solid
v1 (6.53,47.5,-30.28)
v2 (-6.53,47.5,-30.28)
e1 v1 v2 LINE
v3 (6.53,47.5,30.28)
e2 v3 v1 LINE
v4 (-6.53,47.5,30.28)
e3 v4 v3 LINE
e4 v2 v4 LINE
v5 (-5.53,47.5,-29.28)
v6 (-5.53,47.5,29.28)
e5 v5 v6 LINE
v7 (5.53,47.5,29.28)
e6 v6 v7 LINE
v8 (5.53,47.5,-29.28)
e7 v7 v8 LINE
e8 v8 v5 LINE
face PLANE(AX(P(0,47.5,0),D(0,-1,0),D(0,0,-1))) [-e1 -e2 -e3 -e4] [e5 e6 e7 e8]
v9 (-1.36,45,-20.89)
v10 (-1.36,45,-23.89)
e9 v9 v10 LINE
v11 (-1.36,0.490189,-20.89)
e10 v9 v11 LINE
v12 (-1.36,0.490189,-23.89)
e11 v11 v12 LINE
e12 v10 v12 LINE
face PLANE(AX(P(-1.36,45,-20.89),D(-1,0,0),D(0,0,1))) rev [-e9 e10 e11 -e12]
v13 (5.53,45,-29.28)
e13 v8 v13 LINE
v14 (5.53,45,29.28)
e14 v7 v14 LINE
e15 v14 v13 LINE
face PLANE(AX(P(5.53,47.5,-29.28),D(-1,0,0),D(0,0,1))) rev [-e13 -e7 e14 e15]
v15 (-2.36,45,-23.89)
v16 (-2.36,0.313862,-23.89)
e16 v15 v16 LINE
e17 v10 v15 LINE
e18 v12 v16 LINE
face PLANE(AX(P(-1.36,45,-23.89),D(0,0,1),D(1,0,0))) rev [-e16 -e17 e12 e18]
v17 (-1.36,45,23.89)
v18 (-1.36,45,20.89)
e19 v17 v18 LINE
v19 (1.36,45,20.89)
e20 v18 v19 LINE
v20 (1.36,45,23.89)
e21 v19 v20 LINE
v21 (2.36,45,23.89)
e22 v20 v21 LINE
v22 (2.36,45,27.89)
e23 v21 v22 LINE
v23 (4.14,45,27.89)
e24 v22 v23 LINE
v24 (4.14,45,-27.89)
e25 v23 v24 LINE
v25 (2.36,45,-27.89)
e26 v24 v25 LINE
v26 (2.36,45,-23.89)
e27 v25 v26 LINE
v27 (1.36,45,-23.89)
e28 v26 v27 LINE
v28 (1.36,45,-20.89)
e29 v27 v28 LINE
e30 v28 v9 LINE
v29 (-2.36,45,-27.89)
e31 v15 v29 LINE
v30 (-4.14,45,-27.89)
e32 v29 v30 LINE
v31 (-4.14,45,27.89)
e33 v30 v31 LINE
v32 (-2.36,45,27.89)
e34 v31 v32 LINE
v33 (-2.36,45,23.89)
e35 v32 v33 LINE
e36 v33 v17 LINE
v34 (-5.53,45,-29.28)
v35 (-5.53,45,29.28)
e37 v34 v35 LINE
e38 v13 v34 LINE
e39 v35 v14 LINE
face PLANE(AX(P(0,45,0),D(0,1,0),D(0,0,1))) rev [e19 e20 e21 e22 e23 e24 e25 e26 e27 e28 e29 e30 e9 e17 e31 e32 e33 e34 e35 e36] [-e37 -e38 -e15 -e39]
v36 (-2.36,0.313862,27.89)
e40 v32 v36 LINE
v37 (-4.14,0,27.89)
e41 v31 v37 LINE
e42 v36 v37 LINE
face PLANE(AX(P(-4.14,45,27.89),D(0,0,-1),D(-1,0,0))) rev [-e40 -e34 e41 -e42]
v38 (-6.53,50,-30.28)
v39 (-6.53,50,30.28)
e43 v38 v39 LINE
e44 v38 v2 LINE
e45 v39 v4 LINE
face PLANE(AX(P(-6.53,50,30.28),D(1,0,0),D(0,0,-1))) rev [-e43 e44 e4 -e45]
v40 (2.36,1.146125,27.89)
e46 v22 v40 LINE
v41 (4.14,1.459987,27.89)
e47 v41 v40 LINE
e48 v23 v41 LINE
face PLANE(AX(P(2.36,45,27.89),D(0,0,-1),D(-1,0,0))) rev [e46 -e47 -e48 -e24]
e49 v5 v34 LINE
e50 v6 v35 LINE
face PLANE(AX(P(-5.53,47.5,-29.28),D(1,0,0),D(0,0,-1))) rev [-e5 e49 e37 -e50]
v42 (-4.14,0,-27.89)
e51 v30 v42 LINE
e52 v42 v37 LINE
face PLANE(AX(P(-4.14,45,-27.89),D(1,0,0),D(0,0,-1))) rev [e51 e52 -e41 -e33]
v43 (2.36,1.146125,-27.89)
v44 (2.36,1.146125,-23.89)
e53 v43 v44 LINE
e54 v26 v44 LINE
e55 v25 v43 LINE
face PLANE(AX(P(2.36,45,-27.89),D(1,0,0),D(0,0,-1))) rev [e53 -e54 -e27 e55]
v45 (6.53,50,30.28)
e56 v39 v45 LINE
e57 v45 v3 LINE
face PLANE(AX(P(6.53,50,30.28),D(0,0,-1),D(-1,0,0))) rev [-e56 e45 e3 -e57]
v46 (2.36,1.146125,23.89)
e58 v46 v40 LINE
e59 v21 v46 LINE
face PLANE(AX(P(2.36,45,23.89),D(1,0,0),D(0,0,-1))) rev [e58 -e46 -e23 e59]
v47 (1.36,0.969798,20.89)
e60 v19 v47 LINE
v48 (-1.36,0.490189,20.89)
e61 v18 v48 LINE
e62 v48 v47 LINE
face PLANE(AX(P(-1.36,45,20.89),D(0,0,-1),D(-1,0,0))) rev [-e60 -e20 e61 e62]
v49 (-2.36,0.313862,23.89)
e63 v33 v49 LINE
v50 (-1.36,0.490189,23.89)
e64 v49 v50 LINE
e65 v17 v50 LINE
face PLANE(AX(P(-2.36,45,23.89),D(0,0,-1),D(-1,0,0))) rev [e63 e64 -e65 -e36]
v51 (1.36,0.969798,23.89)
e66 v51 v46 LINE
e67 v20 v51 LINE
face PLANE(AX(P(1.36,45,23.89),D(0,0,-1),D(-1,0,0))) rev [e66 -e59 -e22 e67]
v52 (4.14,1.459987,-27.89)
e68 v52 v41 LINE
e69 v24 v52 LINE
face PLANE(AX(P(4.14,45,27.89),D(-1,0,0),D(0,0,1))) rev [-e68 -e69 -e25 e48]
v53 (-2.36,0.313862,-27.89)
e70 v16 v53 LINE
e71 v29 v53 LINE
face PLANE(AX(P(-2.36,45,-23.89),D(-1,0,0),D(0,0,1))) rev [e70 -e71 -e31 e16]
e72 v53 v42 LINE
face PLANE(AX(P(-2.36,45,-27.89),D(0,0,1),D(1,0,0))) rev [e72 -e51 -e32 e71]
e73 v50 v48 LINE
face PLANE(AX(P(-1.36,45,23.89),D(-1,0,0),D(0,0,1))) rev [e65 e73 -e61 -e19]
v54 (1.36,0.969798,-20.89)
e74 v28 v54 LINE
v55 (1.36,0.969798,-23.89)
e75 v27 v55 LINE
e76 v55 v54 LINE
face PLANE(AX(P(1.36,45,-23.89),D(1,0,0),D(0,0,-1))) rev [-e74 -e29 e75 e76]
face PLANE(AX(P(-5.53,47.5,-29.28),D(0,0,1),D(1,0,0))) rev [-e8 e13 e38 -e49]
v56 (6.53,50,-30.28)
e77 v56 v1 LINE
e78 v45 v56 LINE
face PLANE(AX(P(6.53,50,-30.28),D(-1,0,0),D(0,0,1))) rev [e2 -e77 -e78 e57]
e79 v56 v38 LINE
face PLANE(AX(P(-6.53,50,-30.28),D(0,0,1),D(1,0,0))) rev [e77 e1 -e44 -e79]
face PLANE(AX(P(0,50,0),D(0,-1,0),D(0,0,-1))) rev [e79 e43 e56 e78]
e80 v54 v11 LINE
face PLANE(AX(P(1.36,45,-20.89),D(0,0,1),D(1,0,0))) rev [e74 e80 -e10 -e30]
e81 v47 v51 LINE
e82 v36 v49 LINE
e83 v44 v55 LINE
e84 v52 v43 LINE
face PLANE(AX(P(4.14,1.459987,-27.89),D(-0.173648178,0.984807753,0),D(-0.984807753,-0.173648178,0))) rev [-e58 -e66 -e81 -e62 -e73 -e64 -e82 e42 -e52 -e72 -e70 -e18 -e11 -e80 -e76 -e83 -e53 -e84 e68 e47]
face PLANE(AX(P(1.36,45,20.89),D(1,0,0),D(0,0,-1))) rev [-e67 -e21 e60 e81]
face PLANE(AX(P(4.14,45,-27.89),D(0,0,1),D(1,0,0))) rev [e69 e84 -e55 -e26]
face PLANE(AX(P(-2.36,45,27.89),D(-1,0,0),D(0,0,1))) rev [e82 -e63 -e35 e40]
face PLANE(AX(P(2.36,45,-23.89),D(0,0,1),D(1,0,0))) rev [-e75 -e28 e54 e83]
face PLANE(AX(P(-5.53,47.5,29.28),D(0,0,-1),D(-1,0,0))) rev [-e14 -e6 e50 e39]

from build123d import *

# Parameters (mm, degrees)
BOSS_EXTRUDE1_DEPTH = 45
CUT_EXTRUDE1_DEPTH  = 72.788216303
SKETCH3_W           = 11.06
SKETCH3_H           = 58.56
BOSS_EXTRUDE2_DEPTH = 2.5
SKETCH4_W           = 13.06
SKETCH4_H           = 60.56
BOSS_EXTRUDE3_DEPTH = 2.5


with BuildPart() as part:
    # Sketch1 → Boss-Extrude1 (new body)
    with BuildSketch(Plane(origin=(0, 0, 0), x_dir=(1, 0, 0), z_dir=(0, 1, 0))):
        Polygon((-4.14, 27.89), (-4.14, -27.89), (-2.36, -27.89), (-2.36, -23.89), (-1.36, -23.89), (-1.36, -20.89), (1.36, -20.89), (1.36, -23.89), (2.36, -23.89), (2.36, -27.89), (4.14, -27.89), (4.14, 27.89), (2.36, 27.89), (2.36, 23.89), (1.36, 23.89), (1.36, 20.89), (-1.36, 20.89), (-1.36, 23.89), (-2.36, 23.89), (-2.36, 27.89), align=None)
    extrude(amount=BOSS_EXTRUDE1_DEPTH)

    # Sketch2 → Cut-Extrude1 (cut, through all)
    with BuildSketch(Plane.XY.offset(27.89)):
        Polygon((-4.14, 0), (4.14, 0), (4.14, 1.4599874), align=None)
    extrude(amount=-CUT_EXTRUDE1_DEPTH, mode=Mode.SUBTRACT)

    # Sketch3 → Boss-Extrude2 (add)
    with BuildSketch(Plane(origin=(0, 45, 0), x_dir=(1, 0, 0), z_dir=(0, 1, 0))):
        Rectangle(SKETCH3_W, SKETCH3_H)
    extrude(amount=BOSS_EXTRUDE2_DEPTH)

    # Sketch4 → Boss-Extrude3 (add)
    with BuildSketch(Plane(origin=(0, 47.5, 0), x_dir=(1, 0, 0), z_dir=(0, 1, 0))):
        Rectangle(SKETCH4_W, SKETCH4_H)
    extrude(amount=BOSS_EXTRUDE3_DEPTH)


solid = part.part
